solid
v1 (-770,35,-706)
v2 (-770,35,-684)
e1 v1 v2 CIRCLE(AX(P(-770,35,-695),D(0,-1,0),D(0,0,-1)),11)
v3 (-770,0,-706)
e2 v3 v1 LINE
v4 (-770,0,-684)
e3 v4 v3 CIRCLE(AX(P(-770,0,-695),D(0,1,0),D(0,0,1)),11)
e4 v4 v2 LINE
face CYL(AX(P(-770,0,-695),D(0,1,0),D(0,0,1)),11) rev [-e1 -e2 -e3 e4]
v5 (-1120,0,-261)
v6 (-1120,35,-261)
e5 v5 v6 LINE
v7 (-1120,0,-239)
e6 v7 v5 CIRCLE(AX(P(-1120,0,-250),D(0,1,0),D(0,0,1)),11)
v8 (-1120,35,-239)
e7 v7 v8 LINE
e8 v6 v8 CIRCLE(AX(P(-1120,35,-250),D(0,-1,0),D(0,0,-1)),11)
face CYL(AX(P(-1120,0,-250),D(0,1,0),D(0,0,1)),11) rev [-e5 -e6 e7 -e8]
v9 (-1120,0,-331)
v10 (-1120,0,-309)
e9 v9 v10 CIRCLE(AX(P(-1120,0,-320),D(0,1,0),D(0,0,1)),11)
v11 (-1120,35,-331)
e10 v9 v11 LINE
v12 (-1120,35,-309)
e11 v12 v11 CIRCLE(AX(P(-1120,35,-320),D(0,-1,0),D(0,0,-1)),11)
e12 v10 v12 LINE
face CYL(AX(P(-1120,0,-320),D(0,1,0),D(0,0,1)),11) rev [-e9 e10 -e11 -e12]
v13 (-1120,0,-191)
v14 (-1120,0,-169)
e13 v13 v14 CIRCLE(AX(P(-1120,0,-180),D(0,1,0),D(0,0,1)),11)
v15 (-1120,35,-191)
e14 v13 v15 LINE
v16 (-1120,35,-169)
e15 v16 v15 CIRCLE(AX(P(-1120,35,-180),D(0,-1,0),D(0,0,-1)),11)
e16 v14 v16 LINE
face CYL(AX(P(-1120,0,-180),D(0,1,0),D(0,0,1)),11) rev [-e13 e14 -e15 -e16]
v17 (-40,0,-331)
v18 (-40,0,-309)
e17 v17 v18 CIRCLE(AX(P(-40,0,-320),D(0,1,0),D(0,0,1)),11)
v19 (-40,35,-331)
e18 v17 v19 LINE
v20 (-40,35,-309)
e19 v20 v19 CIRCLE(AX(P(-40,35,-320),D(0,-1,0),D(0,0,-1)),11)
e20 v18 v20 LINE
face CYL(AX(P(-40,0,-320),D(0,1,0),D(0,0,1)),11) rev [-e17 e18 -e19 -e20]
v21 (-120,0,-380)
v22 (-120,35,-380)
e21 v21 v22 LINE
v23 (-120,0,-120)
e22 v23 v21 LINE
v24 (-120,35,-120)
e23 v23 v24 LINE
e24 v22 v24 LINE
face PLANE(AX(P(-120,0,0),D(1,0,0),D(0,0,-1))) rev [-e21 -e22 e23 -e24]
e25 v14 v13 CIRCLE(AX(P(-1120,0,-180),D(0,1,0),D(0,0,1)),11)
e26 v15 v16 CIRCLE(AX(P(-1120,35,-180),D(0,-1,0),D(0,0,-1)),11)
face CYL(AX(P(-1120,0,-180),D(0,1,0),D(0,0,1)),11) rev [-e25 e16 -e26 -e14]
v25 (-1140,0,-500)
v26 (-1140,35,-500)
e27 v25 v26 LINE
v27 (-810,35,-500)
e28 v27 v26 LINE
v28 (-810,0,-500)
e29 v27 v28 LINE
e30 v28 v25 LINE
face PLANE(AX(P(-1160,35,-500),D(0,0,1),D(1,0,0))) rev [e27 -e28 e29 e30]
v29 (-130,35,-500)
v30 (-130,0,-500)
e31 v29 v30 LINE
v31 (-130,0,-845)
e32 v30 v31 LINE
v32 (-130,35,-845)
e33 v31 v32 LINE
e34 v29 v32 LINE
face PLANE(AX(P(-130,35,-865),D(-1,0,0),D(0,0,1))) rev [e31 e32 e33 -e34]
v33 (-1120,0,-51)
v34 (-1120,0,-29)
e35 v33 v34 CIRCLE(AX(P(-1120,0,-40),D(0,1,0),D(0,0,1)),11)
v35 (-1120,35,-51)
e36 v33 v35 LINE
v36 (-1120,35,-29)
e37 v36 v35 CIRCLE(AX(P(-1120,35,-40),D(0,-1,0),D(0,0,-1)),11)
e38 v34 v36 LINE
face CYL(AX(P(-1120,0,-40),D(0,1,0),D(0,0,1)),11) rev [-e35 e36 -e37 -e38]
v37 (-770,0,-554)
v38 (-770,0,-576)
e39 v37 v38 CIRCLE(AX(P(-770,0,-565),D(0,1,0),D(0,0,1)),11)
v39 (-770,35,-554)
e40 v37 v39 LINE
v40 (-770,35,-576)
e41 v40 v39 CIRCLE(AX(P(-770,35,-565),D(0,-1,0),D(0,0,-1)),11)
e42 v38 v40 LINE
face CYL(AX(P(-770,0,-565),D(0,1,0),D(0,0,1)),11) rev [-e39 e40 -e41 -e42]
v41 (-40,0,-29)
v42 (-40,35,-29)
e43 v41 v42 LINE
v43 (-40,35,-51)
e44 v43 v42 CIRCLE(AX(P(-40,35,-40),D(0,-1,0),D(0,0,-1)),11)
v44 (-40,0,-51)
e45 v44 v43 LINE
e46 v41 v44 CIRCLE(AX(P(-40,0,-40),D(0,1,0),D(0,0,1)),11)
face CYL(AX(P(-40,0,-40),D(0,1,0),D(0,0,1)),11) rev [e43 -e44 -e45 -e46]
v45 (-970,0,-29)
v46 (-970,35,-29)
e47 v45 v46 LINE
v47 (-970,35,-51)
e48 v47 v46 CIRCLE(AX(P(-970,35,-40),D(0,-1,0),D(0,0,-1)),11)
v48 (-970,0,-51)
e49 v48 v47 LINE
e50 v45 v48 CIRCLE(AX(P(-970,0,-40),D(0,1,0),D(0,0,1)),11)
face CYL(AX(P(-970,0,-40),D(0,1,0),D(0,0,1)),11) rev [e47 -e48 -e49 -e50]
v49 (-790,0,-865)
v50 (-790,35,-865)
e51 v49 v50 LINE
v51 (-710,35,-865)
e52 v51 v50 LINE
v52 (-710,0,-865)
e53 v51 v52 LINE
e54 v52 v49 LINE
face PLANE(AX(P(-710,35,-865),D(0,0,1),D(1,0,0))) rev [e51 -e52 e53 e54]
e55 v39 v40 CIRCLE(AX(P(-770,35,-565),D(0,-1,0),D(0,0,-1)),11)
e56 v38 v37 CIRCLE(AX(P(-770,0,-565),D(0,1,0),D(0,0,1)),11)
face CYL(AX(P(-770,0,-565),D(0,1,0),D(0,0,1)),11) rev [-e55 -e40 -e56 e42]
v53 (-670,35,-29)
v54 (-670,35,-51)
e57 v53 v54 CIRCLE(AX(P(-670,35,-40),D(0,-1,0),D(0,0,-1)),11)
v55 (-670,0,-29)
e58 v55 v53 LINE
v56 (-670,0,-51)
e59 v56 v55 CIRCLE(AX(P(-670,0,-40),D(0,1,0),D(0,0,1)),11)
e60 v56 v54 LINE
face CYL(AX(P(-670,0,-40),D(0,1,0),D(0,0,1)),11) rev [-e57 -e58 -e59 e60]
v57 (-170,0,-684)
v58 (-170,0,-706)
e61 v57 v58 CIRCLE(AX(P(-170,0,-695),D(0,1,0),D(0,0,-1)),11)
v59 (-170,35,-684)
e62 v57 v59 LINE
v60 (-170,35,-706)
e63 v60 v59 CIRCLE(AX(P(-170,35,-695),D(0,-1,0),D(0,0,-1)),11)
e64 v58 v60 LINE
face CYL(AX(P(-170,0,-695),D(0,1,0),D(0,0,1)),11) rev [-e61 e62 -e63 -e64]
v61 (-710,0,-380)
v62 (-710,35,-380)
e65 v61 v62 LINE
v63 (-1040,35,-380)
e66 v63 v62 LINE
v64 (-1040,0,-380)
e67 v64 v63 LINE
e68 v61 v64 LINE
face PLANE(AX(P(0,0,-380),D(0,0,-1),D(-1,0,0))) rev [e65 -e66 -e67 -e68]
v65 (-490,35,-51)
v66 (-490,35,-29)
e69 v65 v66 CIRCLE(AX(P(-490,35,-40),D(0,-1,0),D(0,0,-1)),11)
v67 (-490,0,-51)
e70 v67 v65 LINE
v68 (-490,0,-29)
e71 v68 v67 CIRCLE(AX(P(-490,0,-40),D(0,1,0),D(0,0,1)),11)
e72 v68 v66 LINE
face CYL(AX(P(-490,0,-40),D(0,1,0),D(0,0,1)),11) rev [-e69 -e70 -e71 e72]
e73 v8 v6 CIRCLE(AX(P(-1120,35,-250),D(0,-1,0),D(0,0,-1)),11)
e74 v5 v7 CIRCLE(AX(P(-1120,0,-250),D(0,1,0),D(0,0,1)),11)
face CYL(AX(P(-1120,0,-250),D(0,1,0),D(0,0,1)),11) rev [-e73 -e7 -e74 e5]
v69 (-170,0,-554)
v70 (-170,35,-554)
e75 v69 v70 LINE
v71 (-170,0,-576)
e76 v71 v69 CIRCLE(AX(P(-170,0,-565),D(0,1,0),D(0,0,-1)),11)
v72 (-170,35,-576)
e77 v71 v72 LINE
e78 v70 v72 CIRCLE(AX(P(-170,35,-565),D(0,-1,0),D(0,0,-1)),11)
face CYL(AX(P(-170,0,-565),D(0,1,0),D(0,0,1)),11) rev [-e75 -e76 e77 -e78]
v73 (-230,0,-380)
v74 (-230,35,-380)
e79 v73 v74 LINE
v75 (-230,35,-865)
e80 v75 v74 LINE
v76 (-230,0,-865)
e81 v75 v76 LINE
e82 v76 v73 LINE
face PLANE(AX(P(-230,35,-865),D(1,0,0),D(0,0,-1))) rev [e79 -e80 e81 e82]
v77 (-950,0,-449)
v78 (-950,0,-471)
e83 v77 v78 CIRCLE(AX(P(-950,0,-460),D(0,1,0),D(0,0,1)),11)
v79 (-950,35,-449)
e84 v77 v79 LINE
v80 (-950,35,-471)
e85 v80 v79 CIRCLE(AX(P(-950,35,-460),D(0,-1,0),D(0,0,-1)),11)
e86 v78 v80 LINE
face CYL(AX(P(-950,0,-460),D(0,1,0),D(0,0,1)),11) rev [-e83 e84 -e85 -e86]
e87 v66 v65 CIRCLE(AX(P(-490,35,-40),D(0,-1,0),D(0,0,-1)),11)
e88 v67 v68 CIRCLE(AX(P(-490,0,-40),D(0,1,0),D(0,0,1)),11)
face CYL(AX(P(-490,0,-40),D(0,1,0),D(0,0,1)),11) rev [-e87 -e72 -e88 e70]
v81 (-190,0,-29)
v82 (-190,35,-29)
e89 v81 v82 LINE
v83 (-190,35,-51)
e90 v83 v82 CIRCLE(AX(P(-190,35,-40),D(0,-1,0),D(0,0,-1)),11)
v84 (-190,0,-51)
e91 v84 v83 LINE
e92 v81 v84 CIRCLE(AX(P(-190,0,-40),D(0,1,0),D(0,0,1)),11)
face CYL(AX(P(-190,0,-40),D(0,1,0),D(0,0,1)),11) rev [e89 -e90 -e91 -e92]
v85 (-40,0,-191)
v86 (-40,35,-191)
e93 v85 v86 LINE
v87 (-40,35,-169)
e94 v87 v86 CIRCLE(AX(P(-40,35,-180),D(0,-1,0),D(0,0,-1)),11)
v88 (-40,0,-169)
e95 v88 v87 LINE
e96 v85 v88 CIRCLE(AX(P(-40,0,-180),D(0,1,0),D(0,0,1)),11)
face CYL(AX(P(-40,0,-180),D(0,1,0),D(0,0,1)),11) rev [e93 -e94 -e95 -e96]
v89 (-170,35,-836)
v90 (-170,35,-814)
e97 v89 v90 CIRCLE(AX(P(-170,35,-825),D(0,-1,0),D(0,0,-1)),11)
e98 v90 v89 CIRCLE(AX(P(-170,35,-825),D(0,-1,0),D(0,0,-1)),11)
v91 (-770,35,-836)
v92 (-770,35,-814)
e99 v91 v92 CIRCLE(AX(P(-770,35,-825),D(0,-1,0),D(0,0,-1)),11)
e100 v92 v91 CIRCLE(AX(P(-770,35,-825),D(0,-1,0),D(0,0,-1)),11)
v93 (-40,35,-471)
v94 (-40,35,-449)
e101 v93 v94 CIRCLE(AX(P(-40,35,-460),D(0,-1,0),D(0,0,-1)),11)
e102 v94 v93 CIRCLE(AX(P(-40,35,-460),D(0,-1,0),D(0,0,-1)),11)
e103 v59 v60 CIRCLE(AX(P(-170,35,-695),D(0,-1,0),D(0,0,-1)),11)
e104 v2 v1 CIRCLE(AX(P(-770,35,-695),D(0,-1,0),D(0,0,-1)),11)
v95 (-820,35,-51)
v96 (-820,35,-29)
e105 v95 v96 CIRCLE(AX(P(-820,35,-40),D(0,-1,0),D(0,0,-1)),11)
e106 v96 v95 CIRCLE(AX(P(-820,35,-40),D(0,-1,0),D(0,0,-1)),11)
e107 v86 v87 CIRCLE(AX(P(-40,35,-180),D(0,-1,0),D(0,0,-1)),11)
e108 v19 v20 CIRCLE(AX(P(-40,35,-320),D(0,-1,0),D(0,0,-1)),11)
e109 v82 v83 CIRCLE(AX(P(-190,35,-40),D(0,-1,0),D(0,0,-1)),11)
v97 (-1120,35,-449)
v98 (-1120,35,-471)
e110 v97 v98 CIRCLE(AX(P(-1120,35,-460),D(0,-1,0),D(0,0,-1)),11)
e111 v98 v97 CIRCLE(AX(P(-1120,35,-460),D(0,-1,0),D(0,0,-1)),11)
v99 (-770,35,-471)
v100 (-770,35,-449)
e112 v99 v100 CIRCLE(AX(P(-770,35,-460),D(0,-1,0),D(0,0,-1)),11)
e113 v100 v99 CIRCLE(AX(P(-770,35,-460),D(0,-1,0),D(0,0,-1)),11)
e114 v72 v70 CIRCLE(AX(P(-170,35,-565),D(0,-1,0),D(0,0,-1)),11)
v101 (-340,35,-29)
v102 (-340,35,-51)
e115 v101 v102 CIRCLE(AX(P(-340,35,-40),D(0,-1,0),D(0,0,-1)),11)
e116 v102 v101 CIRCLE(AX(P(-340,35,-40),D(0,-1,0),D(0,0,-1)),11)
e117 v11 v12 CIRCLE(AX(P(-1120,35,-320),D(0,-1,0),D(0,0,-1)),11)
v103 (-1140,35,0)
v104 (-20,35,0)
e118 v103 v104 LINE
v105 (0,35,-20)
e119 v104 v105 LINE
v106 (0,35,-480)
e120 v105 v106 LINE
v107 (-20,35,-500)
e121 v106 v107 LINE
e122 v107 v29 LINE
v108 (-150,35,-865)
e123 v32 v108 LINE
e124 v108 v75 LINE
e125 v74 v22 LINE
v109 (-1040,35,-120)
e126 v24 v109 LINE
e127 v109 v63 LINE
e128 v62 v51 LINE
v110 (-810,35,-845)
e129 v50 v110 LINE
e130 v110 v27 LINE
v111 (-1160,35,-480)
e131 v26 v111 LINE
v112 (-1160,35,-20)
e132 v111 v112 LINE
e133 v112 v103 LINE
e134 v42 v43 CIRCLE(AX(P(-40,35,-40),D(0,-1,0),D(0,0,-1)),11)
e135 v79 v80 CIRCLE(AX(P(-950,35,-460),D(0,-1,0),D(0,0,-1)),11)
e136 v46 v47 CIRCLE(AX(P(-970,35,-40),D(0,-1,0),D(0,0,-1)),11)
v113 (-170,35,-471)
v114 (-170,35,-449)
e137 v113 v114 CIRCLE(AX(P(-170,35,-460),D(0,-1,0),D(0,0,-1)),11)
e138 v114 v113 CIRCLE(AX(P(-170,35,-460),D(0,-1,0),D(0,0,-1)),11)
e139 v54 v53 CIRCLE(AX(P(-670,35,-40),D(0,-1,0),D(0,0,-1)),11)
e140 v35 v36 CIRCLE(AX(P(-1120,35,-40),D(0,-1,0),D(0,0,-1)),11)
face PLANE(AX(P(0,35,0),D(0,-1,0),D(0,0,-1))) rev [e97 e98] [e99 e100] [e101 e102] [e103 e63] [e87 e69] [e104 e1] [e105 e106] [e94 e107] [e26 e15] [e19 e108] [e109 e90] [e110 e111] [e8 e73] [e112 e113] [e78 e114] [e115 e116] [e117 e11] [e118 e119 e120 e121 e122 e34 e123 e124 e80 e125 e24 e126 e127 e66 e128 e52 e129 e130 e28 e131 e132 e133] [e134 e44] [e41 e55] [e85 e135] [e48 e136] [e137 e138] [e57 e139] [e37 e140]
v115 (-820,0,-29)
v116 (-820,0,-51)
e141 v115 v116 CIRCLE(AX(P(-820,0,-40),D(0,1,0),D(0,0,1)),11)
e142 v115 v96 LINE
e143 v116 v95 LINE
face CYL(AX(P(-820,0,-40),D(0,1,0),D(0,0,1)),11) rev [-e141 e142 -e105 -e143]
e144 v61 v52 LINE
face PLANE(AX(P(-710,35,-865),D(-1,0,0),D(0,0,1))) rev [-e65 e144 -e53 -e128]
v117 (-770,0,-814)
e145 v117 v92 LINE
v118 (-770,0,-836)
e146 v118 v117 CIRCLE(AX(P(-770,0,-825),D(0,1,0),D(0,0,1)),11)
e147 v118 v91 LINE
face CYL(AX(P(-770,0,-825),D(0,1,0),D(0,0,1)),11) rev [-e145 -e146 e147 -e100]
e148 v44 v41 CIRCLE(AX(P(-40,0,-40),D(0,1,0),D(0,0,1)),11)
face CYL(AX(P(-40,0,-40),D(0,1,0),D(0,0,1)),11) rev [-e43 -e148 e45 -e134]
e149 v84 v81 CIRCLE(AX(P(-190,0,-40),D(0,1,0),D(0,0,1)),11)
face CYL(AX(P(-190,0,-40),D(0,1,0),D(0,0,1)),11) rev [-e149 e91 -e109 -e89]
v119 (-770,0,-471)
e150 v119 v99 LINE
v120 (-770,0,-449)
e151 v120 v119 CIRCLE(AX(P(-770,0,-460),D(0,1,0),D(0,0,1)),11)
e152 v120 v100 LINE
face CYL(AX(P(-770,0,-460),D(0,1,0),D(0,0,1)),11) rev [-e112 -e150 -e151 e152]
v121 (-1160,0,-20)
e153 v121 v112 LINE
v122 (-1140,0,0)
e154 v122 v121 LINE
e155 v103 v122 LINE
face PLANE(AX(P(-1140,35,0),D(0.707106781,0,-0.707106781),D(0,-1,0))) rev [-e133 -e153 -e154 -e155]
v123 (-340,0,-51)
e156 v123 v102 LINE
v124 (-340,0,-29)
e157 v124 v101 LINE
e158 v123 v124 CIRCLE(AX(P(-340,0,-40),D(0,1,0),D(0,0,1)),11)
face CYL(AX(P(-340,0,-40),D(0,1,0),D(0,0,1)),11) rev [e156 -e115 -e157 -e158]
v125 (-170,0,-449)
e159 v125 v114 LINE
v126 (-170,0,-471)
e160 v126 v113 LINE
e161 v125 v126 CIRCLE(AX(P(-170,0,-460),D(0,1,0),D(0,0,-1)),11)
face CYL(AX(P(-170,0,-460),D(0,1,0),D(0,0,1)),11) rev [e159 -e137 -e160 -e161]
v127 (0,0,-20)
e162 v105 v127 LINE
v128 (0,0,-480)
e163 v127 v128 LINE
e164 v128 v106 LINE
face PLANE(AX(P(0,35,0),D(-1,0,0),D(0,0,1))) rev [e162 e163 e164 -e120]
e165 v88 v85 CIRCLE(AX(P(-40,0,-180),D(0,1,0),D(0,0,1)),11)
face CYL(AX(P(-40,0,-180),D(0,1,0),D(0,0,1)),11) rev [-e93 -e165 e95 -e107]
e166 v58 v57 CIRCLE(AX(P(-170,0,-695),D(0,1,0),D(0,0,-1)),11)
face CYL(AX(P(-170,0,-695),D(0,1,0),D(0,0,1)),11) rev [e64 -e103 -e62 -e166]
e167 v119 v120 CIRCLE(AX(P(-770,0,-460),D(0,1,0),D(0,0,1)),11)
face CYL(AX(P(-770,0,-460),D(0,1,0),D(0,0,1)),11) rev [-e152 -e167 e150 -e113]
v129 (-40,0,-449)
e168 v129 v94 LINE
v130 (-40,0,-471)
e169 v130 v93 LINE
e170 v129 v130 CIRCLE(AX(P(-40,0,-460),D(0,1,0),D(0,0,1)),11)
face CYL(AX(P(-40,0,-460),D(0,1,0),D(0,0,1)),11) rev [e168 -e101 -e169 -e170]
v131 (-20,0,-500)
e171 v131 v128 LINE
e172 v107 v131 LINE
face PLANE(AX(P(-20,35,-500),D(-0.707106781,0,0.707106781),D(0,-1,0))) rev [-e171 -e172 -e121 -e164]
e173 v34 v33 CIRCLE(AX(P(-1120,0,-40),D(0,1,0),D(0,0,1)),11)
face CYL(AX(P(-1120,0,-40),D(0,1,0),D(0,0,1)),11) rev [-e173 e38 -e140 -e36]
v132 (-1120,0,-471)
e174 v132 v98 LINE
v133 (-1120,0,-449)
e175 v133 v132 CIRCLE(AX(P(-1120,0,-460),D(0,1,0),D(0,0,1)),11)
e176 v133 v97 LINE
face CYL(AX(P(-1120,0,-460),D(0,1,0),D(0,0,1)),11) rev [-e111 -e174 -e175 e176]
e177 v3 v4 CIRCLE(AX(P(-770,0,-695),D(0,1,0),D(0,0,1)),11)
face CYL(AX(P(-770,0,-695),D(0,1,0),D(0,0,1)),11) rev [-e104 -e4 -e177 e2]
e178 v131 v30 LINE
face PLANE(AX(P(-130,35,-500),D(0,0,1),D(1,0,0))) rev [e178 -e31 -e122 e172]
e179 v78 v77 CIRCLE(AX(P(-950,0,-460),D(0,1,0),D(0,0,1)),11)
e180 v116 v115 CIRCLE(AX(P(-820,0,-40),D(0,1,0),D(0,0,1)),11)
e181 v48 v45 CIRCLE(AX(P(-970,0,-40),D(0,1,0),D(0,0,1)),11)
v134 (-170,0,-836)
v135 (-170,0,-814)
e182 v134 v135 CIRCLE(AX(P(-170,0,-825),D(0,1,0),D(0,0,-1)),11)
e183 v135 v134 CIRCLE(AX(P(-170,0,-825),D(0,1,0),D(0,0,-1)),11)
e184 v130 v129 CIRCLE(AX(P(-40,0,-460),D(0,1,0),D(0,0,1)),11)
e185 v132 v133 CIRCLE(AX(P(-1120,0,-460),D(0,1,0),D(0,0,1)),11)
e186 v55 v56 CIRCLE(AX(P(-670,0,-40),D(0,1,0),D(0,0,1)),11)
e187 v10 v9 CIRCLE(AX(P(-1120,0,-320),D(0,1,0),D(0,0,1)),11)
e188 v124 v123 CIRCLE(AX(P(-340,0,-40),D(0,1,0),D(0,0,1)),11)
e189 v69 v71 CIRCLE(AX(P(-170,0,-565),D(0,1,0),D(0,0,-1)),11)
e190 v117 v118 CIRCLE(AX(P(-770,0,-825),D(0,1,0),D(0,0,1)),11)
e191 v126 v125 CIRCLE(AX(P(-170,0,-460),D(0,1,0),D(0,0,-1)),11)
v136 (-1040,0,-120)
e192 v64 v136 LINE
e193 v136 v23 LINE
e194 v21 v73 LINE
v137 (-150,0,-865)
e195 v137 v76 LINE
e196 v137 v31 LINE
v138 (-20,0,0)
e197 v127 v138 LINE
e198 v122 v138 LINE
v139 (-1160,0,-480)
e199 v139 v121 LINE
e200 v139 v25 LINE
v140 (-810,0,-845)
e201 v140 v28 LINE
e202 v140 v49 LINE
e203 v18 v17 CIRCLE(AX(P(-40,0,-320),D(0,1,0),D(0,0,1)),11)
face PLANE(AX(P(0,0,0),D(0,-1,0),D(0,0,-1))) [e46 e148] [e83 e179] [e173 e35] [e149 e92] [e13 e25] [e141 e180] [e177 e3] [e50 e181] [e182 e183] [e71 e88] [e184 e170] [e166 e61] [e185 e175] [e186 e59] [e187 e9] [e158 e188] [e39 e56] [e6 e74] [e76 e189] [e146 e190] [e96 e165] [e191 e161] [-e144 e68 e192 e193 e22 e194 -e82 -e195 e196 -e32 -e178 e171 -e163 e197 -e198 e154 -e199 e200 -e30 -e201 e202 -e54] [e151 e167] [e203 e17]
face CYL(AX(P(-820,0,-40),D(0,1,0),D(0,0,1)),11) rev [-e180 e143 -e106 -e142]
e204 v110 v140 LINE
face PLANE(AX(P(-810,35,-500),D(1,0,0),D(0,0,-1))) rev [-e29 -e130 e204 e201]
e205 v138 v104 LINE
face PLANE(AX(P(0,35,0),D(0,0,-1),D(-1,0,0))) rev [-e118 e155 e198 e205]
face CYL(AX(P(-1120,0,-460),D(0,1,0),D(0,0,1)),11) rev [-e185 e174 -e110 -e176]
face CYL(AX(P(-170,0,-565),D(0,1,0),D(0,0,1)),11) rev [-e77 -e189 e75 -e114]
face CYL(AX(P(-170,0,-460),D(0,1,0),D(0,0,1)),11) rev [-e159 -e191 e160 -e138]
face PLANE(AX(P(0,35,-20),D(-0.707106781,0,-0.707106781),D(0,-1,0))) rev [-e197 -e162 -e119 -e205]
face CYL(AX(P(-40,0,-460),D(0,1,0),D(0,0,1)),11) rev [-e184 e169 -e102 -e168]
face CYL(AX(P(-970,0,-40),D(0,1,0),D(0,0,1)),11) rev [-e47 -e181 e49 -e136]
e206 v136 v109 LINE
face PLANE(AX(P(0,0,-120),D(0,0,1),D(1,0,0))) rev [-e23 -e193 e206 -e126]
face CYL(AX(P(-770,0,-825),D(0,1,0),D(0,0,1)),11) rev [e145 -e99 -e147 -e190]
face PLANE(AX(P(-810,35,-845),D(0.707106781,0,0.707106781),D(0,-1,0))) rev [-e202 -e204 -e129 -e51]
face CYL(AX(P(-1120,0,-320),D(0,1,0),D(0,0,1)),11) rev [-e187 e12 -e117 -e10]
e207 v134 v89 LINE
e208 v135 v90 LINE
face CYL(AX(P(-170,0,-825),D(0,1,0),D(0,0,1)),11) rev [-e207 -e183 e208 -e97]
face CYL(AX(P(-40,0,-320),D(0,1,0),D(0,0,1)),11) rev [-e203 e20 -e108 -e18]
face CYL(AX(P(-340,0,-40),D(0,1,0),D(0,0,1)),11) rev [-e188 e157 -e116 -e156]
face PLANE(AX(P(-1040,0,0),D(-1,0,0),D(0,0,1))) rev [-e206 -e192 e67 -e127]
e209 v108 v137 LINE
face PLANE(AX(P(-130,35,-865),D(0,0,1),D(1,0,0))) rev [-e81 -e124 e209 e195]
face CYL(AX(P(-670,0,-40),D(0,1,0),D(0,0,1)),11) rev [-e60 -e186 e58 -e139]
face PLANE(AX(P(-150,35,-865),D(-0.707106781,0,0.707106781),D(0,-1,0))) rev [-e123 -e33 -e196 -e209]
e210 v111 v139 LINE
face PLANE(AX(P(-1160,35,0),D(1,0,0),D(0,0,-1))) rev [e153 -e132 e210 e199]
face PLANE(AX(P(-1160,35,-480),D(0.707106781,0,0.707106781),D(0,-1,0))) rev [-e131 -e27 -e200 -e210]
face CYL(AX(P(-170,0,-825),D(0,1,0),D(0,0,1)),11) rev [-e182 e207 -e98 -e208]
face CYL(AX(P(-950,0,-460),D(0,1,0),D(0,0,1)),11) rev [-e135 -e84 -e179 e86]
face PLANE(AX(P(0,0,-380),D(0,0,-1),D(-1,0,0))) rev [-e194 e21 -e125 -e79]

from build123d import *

# Parameters (mm, degrees)
EXTRUDE_1_DEPTH          = 35
CUT_EXTRUDE_1_DEPTH      = 1448.428754723
CUT_EXTRUDE_1_DEPTH_BACK = 1448.428754723
CHAMFER_2_SIZE           = 20
CUT_EXTRUDE_2_DEPTH      = 1448.428754723
CUT_EXTRUDE_2_DEPTH_BACK = 1448.428754723
SKETCH_5_R               = 11


with BuildPart() as part:
    # 草图1 → 凸台-拉伸1 (new body)
    with BuildSketch(Plane(origin=(0, 0, 0), x_dir=(1, 0, 0), z_dir=(0, 1, 0))):
        Polygon((-1160, 500), (-810, 500), (-810, 865), (-710, 865), (-710, 745), (-230, 745), (-230, 865), (-130, 865), (-130, 500), (0, 500), (0, 0), (-1160, 0), align=None)
    extrude(amount=EXTRUDE_1_DEPTH)

    # 草图4 → 切除-拉伸1 (cut, two sides: drawn at the far end of the back side and taken through both)
    with BuildSketch(Plane(origin=(0, 35, 0), x_dir=(1, 0, 0), z_dir=(0, 1, 0)).offset(-CUT_EXTRUDE_1_DEPTH_BACK)):
        Polygon((-230, 745), (-710, 745), (-710, 380), (-1040, 380), (-1040, 120), (-120, 120), (-120, 380), (-230, 380), align=None)
    extrude(amount=CUT_EXTRUDE_1_DEPTH + CUT_EXTRUDE_1_DEPTH_BACK, mode=Mode.SUBTRACT)

    # 倒角2
    chamfer_2_edges = [part.edges().sort_by_distance(p)[0] for p in [
        (0, 17.5, 0),
        (-1160, 17.5, 0),
        (-1160, 17.5, -500),
        (-810, 17.5, -865),
        (-130, 17.5, -865),
        (0, 17.5, -500),
    ]]
    chamfer(chamfer_2_edges, length=CHAMFER_2_SIZE)

    # 草图5 → 切除-拉伸2 (cut, two sides: drawn at the far end of the back side and taken through both)
    with BuildSketch(Plane(origin=(0, 35, 0), x_dir=(1, 0, 0), z_dir=(0, 1, 0)).offset(-CUT_EXTRUDE_2_DEPTH_BACK)):
        with Locations(Location((-1120, 40, 0), (0, 0, 270))):
            Circle(SKETCH_5_R)
        with Locations(Location((-970, 40, 0), (0, 0, 270))):
            Circle(SKETCH_5_R)
        with Locations(Location((-820, 40, 0), (0, 0, 270))):
            Circle(SKETCH_5_R)
        with Locations(Location((-670, 40, 0), (0, 0, 270))):
            Circle(SKETCH_5_R)
        with Locations(Location((-490, 40, 0), (0, 0, 270))):
            Circle(SKETCH_5_R)
        with Locations(Location((-340, 40, 0), (0, 0, 270))):
            Circle(SKETCH_5_R)
        with Locations(Location((-190, 40, 0), (0, 0, 270))):
            Circle(SKETCH_5_R)
        with Locations(Location((-40, 40, 0), (0, 0, 270))):
            Circle(SKETCH_5_R)
        with Locations(Location((-770, 825, 0), (0, 0, 270))):
            Circle(SKETCH_5_R)
        with Locations(Location((-770, 695, 0), (0, 0, 270))):
            Circle(SKETCH_5_R)
        with Locations(Location((-770, 565, 0), (0, 0, 270))):
            Circle(SKETCH_5_R)
        with Locations(Location((-770, 460, 0), (0, 0, 270))):
            Circle(SKETCH_5_R)
        with Locations(Location((-1120, 180, 0), (0, 0, 270))):
            Circle(SKETCH_5_R)
        with Locations(Location((-1120, 250, 0), (0, 0, 270))):
            Circle(SKETCH_5_R)
        with Locations(Location((-1120, 320, 0), (0, 0, 270))):
            Circle(SKETCH_5_R)
        with Locations(Location((-1120, 460, 0), (0, 0, 270))):
            Circle(SKETCH_5_R)
        with Locations(Location((-950, 460, 0), (0, 0, 270))):
            Circle(SKETCH_5_R)
        with Locations(Location((-170, 460, 0), (0, 0, 90))):
            Circle(SKETCH_5_R)
        with Locations(Location((-170, 565, 0), (0, 0, 90))):
            Circle(SKETCH_5_R)
        with Locations(Location((-170, 695, 0), (0, 0, 90))):
            Circle(SKETCH_5_R)
        with Locations(Location((-170, 825, 0), (0, 0, 90))):
            Circle(SKETCH_5_R)
        with Locations(Location((-40, 460, 0), (0, 0, 270))):
            Circle(SKETCH_5_R)
        with Locations(Location((-40, 320, 0), (0, 0, 270))):
            Circle(SKETCH_5_R)
        with Locations(Location((-40, 180, 0), (0, 0, 270))):
            Circle(SKETCH_5_R)
    extrude(amount=CUT_EXTRUDE_2_DEPTH + CUT_EXTRUDE_2_DEPTH_BACK, mode=Mode.SUBTRACT)


solid = part.part
